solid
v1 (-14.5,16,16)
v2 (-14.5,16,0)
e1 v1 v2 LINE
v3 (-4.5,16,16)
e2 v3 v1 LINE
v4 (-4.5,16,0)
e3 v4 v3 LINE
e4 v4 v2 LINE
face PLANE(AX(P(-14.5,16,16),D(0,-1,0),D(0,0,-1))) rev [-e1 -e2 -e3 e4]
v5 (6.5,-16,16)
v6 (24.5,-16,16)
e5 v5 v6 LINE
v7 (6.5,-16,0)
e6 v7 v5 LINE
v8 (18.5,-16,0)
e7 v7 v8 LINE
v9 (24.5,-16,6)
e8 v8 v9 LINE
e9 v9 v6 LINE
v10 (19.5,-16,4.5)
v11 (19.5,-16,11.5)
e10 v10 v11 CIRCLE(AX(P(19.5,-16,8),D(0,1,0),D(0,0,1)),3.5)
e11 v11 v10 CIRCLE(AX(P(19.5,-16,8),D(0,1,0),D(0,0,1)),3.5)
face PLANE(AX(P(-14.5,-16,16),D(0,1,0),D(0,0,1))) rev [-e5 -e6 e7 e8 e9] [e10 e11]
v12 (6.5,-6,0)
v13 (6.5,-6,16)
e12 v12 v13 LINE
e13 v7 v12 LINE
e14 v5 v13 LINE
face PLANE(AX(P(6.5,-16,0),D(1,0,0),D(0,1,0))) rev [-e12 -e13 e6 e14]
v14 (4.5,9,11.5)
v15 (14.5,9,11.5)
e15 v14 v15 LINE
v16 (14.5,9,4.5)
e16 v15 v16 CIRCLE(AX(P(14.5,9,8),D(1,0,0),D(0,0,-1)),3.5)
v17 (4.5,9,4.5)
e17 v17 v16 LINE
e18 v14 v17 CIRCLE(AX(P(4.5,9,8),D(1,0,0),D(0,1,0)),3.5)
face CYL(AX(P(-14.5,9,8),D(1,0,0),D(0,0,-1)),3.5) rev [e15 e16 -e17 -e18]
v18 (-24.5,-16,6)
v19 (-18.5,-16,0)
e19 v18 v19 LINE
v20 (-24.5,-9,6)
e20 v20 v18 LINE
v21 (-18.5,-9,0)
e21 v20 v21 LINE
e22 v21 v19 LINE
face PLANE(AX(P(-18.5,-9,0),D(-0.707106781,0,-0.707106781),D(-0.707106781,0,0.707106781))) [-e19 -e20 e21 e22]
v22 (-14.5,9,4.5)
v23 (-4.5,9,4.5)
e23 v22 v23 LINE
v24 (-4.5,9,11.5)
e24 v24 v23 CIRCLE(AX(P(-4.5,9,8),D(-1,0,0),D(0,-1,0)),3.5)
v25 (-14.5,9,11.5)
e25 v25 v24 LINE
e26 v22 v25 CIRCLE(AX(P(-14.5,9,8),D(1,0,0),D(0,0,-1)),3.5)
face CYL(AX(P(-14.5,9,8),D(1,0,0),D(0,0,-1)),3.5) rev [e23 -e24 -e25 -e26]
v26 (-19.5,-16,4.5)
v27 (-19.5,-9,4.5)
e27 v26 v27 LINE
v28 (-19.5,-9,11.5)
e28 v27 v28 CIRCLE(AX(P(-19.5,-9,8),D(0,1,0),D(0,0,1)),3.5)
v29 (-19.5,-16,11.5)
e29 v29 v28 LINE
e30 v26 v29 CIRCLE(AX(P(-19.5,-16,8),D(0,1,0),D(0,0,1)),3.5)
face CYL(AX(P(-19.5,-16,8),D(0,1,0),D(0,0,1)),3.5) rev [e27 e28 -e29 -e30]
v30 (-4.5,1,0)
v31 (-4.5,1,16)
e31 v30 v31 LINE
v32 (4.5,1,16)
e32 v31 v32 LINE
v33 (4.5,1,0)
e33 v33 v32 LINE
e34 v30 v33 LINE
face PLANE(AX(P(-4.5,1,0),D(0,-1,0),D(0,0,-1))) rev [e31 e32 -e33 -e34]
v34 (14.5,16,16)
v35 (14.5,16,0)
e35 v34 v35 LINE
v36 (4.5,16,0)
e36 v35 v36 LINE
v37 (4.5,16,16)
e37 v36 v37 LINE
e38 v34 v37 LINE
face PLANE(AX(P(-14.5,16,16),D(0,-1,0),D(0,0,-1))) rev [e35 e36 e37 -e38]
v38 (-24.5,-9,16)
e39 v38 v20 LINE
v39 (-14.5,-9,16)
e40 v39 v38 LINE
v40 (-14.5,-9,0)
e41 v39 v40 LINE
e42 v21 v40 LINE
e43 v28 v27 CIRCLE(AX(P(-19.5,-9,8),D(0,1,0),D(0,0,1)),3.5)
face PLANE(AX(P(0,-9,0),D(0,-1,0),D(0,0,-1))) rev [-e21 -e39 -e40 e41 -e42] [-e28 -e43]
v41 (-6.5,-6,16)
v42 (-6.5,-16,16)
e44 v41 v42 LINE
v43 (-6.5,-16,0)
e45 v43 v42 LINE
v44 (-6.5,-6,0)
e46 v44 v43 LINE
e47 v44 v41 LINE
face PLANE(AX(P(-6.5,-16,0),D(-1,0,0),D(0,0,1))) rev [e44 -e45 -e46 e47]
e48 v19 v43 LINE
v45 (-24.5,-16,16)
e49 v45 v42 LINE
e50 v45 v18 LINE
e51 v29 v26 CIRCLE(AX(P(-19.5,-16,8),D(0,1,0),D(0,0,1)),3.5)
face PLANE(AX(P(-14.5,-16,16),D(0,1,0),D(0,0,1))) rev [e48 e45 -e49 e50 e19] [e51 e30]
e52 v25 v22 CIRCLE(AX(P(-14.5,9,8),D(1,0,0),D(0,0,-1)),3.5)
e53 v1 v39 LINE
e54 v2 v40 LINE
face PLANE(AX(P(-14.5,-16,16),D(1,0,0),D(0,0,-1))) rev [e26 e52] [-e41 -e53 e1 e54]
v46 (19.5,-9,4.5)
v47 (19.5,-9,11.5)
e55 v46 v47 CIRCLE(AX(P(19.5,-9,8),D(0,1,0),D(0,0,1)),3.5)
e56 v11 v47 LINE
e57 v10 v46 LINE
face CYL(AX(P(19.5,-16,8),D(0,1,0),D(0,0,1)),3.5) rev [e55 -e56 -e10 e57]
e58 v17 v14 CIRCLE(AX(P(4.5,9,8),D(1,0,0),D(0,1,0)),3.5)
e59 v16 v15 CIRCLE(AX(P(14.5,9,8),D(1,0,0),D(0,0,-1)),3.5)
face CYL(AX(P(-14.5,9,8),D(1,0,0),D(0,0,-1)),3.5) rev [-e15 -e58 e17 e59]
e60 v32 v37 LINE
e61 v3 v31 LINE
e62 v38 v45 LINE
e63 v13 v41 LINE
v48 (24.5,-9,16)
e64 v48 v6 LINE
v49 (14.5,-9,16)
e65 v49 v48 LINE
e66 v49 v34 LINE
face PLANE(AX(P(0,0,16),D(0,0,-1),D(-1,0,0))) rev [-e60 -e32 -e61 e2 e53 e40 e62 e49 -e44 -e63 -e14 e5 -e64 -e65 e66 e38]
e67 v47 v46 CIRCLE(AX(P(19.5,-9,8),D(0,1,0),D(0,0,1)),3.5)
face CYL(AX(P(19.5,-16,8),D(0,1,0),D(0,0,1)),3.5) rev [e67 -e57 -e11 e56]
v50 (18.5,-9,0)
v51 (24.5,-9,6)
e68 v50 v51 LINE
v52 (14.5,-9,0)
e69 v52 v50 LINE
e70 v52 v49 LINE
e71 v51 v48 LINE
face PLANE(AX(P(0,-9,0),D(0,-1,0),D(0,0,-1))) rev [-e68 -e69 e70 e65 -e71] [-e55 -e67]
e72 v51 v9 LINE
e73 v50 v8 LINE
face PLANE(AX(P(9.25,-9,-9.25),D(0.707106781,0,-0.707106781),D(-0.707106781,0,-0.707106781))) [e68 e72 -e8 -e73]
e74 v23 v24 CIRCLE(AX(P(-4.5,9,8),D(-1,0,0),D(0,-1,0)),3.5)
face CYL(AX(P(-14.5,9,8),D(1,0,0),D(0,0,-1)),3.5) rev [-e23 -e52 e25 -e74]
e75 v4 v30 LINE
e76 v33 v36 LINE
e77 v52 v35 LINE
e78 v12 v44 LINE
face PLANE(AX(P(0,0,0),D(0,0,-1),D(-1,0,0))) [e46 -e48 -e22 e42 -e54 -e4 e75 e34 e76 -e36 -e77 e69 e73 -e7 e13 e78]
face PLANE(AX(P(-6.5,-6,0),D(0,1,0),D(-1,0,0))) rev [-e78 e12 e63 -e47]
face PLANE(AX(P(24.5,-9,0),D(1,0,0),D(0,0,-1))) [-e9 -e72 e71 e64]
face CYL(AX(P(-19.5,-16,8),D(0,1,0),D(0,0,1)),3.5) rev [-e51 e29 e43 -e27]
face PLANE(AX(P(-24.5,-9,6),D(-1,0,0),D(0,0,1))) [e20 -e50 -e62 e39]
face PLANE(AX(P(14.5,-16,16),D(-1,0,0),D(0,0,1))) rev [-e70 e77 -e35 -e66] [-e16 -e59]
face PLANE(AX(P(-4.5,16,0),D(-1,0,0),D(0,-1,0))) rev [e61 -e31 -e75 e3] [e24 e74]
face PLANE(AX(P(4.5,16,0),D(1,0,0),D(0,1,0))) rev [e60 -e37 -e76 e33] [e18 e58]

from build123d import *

# Parameters (mm, degrees)
BASE_PROFILE_SKETCH_W     = 29
BASE_PROFILE_SKETCH_H     = 32
BASE_BLOCK_DEPTH          = 16
CENTRE_SLOT_SKETCH_W      = 13
CENTRE_SLOT_SKETCH_H      = 10
CENTRE_SLOT_DEPTH         = 16
SIDE_NOTCH_SKETCH_W       = 9
SIDE_NOTCH_SKETCH_H       = 15
SIDE_NOTCH_DEPTH          = 27.874709301
FOOT_HOLE_SKETCH_R        = 3.5
FOOT_HOLE_DEPTH           = 37.783148315
UPRIGHT_LUG_1_DEPTH       = 7
UPRIGHT_LUG_2_SKETCH_W    = 8
UPRIGHT_LUG_2_SKETCH_H    = 16
UPRIGHT_LUG_2_DEPTH       = 7
LUG_1_CROSS_HOLE_SKETCH_R = 3.5
LUG_1_CROSS_HOLE_DEPTH    = 7
LUG_2_CROSS_HOLE_SKETCH_R = 3.5
LUG_2_CROSS_HOLE_DEPTH    = 7


with BuildPart() as part:
    # Base Profile Sketch → Base Block (new body)
    with BuildSketch(Plane.XY):
        Rectangle(BASE_PROFILE_SKETCH_W, BASE_PROFILE_SKETCH_H)
    extrude(amount=BASE_BLOCK_DEPTH)

    # Centre Slot Sketch → Centre Slot (cut)
    with BuildSketch(Plane.XY.offset(16)):
        with Locations((0, -11)):
            Rectangle(CENTRE_SLOT_SKETCH_W, CENTRE_SLOT_SKETCH_H)
    extrude(amount=-CENTRE_SLOT_DEPTH, mode=Mode.SUBTRACT)

    # Side Notch Sketch → Side Notch (cut, through all)
    with BuildSketch(Plane.XY.offset(16)):
        with Locations((0, 8.5)):
            Rectangle(SIDE_NOTCH_SKETCH_W, SIDE_NOTCH_SKETCH_H)
    extrude(amount=-SIDE_NOTCH_DEPTH, mode=Mode.SUBTRACT)

    # Foot Hole Sketch → Foot Hole (cut, through all)
    with BuildSketch(Plane(origin=(14.5, 0, 0), x_dir=(0, 0, -1), z_dir=(1, 0, 0))):
        with Locations((-8, 9)):
            Circle(FOOT_HOLE_SKETCH_R)
    extrude(amount=-FOOT_HOLE_DEPTH, mode=Mode.SUBTRACT)

    # Upright Lug 1 Sketch → Upright Lug 1 (add)
    with BuildSketch(Plane.XZ.offset(16)):
        Polygon((-18.5, 0), (-24.5, 6), (-24.5, 16), (-14.5, 16), (-6.5, 16), (-6.5, 0), (-14.5, 0), align=None)
    extrude(amount=-UPRIGHT_LUG_1_DEPTH)

    # Upright Lug 2 Sketch → Upright Lug 2 (add)
    with BuildSketch(Plane.XZ.offset(16)):
        Polygon((14.5, 0), (18.5, 0), (24.5, 6), (24.5, 16), (14.5, 16), align=None)
        with Locations((10.5, 8)):
            Rectangle(UPRIGHT_LUG_2_SKETCH_W, UPRIGHT_LUG_2_SKETCH_H)
    extrude(amount=-UPRIGHT_LUG_2_DEPTH)

    # Lug 1 Cross Hole Sketch → Lug 1 Cross Hole (cut)
    with BuildSketch(Plane(origin=(0, -9, 0), x_dir=(1, 0, 0), z_dir=(0, 1, 0))):
        with Locations(Location((-19.5, -8, 0), (0, 0, 270))):
            Circle(LUG_1_CROSS_HOLE_SKETCH_R)
    extrude(amount=-LUG_1_CROSS_HOLE_DEPTH, mode=Mode.SUBTRACT)

    # Lug 2 Cross Hole Sketch → Lug 2 Cross Hole (cut)
    with BuildSketch(Plane(origin=(0, -9, 0), x_dir=(1, 0, 0), z_dir=(0, 1, 0))):
        with Locations(Location((19.5, -8, 0), (0, 0, 270))):
            Circle(LUG_2_CROSS_HOLE_SKETCH_R)
    extrude(amount=-LUG_2_CROSS_HOLE_DEPTH, mode=Mode.SUBTRACT)


solid = part.part
